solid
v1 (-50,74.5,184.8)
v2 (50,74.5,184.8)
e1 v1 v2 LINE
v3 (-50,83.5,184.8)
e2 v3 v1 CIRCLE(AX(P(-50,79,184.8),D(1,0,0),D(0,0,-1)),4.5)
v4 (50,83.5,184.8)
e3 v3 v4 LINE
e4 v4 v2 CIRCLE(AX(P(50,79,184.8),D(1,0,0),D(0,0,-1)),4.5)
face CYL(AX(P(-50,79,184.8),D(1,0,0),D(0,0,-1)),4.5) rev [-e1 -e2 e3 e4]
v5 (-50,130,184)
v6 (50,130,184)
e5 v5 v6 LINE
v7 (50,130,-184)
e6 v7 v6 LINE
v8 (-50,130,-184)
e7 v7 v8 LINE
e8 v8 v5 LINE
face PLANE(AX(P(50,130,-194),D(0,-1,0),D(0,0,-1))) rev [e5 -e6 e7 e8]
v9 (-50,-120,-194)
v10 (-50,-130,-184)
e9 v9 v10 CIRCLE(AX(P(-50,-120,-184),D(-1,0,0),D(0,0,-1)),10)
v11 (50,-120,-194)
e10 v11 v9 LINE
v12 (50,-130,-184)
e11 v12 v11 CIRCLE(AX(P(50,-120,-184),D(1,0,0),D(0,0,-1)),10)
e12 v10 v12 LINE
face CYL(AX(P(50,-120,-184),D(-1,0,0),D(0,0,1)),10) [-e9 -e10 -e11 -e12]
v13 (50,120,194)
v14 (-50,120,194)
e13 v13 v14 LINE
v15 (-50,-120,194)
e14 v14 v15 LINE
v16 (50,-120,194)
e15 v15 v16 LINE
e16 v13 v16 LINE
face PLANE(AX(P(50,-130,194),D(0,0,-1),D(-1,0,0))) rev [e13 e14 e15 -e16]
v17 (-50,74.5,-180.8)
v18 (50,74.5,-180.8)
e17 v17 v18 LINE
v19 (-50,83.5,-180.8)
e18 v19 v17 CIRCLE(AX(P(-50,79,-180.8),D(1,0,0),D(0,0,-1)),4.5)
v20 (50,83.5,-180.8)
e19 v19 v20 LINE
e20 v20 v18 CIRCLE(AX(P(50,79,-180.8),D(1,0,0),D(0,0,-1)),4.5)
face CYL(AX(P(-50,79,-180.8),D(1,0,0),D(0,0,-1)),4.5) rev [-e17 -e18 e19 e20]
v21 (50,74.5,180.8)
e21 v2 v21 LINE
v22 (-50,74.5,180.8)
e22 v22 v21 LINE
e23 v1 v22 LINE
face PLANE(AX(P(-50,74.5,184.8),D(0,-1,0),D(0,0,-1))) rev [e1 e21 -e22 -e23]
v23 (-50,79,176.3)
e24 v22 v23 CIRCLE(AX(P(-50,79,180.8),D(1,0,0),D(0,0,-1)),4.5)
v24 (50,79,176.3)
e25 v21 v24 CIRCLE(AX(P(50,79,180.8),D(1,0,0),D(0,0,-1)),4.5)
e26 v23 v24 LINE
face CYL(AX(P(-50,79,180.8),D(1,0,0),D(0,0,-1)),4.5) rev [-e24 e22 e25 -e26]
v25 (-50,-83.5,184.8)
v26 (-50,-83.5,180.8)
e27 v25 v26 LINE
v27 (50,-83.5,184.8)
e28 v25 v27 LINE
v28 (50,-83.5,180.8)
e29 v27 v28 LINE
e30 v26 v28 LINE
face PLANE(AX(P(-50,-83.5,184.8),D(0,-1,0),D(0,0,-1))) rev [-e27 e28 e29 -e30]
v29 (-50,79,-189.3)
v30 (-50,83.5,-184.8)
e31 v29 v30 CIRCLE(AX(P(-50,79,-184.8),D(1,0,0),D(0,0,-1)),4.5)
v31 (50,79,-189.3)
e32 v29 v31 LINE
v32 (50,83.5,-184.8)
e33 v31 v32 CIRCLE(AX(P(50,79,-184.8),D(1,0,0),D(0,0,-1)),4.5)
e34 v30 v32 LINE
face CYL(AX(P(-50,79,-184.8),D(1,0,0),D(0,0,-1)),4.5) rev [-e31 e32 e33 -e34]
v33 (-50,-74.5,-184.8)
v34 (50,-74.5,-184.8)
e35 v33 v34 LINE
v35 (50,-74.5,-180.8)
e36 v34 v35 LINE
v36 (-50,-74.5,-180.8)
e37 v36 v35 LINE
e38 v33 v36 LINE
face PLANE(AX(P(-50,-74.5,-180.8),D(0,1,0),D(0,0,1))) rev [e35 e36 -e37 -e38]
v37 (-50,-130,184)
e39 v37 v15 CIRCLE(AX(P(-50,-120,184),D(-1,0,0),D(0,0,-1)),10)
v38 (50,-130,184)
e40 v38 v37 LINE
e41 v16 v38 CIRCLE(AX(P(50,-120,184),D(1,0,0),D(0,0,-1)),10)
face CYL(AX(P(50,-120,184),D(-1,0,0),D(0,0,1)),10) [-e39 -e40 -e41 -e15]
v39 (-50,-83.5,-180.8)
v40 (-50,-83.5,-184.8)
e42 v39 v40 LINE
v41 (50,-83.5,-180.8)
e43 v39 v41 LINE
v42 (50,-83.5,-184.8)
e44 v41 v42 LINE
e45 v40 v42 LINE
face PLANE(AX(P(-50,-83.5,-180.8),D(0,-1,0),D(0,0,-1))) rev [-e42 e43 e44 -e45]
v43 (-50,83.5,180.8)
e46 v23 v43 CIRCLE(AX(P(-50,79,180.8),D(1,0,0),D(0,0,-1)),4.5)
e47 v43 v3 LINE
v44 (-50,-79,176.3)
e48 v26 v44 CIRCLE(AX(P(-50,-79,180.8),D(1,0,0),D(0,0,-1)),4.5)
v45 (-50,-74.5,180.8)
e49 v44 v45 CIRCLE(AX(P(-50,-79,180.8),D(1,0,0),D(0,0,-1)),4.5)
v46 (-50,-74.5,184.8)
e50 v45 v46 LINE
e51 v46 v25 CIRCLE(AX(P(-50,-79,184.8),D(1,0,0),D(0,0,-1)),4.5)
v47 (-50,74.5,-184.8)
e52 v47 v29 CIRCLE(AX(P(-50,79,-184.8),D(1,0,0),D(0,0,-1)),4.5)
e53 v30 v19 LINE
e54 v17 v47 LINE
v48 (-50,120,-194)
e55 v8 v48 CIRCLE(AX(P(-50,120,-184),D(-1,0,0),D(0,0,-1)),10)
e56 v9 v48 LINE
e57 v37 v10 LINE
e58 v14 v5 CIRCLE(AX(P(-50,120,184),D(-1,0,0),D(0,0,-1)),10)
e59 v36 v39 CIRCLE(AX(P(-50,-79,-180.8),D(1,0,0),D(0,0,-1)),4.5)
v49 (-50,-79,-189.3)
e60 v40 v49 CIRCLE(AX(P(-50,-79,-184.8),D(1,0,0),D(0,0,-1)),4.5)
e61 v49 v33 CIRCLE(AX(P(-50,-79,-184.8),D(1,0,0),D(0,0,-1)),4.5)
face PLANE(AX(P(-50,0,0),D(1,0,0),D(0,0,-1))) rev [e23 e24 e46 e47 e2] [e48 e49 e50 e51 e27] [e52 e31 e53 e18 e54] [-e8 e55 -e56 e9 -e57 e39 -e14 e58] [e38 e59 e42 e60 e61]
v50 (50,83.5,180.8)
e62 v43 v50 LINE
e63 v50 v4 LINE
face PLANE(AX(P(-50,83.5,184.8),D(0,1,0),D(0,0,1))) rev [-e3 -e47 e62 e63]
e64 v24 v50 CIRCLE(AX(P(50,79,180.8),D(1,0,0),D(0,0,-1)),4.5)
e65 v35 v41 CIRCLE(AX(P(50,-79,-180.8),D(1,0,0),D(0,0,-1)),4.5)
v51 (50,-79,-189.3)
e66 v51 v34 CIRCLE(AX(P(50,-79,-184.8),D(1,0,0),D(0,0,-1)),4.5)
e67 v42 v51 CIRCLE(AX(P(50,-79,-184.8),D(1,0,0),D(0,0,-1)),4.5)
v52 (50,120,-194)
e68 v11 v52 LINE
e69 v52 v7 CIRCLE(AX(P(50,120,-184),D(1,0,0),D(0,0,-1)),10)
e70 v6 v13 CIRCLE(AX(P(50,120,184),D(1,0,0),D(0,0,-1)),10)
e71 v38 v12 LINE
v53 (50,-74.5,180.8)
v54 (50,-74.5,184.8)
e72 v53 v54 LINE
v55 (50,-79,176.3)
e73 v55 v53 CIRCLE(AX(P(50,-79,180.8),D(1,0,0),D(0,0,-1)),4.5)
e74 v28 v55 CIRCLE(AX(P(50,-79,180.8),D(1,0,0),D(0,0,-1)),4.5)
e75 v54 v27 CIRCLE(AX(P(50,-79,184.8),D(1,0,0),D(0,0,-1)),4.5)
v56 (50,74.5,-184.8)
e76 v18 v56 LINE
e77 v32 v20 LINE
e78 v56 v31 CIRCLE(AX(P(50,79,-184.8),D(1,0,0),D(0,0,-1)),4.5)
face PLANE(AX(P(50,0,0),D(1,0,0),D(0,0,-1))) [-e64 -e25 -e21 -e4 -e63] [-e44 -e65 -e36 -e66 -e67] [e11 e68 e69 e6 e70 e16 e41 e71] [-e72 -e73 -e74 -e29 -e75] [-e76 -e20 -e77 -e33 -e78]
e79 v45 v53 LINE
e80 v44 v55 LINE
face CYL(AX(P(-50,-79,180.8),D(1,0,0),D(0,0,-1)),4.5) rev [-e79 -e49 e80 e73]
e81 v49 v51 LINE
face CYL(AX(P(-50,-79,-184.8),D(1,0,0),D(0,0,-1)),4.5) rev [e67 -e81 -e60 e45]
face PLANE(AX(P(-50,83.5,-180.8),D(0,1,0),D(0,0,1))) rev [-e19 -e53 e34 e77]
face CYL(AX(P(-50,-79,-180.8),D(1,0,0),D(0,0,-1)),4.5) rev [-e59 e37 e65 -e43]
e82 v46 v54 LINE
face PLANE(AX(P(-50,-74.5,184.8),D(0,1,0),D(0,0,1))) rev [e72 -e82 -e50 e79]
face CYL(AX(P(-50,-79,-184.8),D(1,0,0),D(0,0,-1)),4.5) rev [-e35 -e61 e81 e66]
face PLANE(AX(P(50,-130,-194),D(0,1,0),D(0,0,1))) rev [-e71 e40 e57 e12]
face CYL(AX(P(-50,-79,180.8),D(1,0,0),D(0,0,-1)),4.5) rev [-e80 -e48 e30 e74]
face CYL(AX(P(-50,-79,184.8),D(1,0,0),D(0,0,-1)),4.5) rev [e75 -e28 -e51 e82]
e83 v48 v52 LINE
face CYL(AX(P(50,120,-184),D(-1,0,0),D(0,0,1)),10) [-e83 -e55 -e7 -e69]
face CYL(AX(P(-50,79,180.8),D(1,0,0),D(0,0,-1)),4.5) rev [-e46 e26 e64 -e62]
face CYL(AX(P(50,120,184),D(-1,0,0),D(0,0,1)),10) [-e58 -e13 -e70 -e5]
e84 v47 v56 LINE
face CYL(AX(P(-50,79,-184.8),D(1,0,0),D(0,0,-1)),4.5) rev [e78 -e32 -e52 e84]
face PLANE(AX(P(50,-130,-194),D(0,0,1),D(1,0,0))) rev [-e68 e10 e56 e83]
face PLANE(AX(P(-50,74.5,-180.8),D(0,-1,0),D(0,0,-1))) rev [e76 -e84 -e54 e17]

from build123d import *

# Parameters (mm, degrees)
SKETCH_1_W          = 388
SKETCH_1_H          = 260
EXTRUDE_1_DEPTH     = 50
CUT_EXTRUDE_1_DEPTH = 100
FILLET_1_R          = 10


with BuildPart() as part:
    # 草图1 → 凸台-拉伸1 (new, symmetric)
    with BuildSketch(Plane(origin=(0, 0, 0), x_dir=(0, 0, -1), z_dir=(1, 0, 0))):
        Rectangle(SKETCH_1_W, SKETCH_1_H)
    extrude(amount=EXTRUDE_1_DEPTH, both=True)

    # 草图2 → 切除-拉伸1 (cut)
    with BuildSketch(Plane(origin=(50, 0, 0), x_dir=(0, 0, -1), z_dir=(1, 0, 0))):
        with BuildLine():
            Line((-184.8, 83.5), (-180.8, 83.5))
            ThreePointArc((-180.8, 83.5), (-176.3, 79), (-180.8, 74.5))
            Line((-180.8, 74.5), (-184.8, 74.5))
            ThreePointArc((-184.8, 74.5), (-189.3, 79), (-184.8, 83.5))
        make_face()
        with BuildLine():
            Line((180.8, 83.5), (184.8, 83.5))
            ThreePointArc((184.8, 83.5), (189.3, 79), (184.8, 74.5))
            Line((184.8, 74.5), (180.8, 74.5))
            ThreePointArc((180.8, 74.5), (176.3, 79), (180.8, 83.5))
        make_face()
        with BuildLine():
            Line((180.8, -74.5), (184.8, -74.5))
            ThreePointArc((184.8, -74.5), (189.3, -79), (184.8, -83.5))
            Line((184.8, -83.5), (180.8, -83.5))
            ThreePointArc((180.8, -83.5), (176.3, -79), (180.8, -74.5))
        make_face()
        with BuildLine():
            Line((-184.8, -74.5), (-180.8, -74.5))
            ThreePointArc((-180.8, -74.5), (-176.3, -79), (-180.8, -83.5))
            Line((-180.8, -83.5), (-184.8, -83.5))
            ThreePointArc((-184.8, -83.5), (-189.3, -79), (-184.8, -74.5))
        make_face()
    extrude(amount=-CUT_EXTRUDE_1_DEPTH, mode=Mode.SUBTRACT)

    # 圆角1
    fillet_1_edges = [part.edges().sort_by_distance(p)[0] for p in [
        (0, 130, 194),
        (0, 130, -194),
        (0, -130, -194),
        (0, -130, 194),
    ]]
    fillet(fillet_1_edges, radius=FILLET_1_R)


solid = part.part
